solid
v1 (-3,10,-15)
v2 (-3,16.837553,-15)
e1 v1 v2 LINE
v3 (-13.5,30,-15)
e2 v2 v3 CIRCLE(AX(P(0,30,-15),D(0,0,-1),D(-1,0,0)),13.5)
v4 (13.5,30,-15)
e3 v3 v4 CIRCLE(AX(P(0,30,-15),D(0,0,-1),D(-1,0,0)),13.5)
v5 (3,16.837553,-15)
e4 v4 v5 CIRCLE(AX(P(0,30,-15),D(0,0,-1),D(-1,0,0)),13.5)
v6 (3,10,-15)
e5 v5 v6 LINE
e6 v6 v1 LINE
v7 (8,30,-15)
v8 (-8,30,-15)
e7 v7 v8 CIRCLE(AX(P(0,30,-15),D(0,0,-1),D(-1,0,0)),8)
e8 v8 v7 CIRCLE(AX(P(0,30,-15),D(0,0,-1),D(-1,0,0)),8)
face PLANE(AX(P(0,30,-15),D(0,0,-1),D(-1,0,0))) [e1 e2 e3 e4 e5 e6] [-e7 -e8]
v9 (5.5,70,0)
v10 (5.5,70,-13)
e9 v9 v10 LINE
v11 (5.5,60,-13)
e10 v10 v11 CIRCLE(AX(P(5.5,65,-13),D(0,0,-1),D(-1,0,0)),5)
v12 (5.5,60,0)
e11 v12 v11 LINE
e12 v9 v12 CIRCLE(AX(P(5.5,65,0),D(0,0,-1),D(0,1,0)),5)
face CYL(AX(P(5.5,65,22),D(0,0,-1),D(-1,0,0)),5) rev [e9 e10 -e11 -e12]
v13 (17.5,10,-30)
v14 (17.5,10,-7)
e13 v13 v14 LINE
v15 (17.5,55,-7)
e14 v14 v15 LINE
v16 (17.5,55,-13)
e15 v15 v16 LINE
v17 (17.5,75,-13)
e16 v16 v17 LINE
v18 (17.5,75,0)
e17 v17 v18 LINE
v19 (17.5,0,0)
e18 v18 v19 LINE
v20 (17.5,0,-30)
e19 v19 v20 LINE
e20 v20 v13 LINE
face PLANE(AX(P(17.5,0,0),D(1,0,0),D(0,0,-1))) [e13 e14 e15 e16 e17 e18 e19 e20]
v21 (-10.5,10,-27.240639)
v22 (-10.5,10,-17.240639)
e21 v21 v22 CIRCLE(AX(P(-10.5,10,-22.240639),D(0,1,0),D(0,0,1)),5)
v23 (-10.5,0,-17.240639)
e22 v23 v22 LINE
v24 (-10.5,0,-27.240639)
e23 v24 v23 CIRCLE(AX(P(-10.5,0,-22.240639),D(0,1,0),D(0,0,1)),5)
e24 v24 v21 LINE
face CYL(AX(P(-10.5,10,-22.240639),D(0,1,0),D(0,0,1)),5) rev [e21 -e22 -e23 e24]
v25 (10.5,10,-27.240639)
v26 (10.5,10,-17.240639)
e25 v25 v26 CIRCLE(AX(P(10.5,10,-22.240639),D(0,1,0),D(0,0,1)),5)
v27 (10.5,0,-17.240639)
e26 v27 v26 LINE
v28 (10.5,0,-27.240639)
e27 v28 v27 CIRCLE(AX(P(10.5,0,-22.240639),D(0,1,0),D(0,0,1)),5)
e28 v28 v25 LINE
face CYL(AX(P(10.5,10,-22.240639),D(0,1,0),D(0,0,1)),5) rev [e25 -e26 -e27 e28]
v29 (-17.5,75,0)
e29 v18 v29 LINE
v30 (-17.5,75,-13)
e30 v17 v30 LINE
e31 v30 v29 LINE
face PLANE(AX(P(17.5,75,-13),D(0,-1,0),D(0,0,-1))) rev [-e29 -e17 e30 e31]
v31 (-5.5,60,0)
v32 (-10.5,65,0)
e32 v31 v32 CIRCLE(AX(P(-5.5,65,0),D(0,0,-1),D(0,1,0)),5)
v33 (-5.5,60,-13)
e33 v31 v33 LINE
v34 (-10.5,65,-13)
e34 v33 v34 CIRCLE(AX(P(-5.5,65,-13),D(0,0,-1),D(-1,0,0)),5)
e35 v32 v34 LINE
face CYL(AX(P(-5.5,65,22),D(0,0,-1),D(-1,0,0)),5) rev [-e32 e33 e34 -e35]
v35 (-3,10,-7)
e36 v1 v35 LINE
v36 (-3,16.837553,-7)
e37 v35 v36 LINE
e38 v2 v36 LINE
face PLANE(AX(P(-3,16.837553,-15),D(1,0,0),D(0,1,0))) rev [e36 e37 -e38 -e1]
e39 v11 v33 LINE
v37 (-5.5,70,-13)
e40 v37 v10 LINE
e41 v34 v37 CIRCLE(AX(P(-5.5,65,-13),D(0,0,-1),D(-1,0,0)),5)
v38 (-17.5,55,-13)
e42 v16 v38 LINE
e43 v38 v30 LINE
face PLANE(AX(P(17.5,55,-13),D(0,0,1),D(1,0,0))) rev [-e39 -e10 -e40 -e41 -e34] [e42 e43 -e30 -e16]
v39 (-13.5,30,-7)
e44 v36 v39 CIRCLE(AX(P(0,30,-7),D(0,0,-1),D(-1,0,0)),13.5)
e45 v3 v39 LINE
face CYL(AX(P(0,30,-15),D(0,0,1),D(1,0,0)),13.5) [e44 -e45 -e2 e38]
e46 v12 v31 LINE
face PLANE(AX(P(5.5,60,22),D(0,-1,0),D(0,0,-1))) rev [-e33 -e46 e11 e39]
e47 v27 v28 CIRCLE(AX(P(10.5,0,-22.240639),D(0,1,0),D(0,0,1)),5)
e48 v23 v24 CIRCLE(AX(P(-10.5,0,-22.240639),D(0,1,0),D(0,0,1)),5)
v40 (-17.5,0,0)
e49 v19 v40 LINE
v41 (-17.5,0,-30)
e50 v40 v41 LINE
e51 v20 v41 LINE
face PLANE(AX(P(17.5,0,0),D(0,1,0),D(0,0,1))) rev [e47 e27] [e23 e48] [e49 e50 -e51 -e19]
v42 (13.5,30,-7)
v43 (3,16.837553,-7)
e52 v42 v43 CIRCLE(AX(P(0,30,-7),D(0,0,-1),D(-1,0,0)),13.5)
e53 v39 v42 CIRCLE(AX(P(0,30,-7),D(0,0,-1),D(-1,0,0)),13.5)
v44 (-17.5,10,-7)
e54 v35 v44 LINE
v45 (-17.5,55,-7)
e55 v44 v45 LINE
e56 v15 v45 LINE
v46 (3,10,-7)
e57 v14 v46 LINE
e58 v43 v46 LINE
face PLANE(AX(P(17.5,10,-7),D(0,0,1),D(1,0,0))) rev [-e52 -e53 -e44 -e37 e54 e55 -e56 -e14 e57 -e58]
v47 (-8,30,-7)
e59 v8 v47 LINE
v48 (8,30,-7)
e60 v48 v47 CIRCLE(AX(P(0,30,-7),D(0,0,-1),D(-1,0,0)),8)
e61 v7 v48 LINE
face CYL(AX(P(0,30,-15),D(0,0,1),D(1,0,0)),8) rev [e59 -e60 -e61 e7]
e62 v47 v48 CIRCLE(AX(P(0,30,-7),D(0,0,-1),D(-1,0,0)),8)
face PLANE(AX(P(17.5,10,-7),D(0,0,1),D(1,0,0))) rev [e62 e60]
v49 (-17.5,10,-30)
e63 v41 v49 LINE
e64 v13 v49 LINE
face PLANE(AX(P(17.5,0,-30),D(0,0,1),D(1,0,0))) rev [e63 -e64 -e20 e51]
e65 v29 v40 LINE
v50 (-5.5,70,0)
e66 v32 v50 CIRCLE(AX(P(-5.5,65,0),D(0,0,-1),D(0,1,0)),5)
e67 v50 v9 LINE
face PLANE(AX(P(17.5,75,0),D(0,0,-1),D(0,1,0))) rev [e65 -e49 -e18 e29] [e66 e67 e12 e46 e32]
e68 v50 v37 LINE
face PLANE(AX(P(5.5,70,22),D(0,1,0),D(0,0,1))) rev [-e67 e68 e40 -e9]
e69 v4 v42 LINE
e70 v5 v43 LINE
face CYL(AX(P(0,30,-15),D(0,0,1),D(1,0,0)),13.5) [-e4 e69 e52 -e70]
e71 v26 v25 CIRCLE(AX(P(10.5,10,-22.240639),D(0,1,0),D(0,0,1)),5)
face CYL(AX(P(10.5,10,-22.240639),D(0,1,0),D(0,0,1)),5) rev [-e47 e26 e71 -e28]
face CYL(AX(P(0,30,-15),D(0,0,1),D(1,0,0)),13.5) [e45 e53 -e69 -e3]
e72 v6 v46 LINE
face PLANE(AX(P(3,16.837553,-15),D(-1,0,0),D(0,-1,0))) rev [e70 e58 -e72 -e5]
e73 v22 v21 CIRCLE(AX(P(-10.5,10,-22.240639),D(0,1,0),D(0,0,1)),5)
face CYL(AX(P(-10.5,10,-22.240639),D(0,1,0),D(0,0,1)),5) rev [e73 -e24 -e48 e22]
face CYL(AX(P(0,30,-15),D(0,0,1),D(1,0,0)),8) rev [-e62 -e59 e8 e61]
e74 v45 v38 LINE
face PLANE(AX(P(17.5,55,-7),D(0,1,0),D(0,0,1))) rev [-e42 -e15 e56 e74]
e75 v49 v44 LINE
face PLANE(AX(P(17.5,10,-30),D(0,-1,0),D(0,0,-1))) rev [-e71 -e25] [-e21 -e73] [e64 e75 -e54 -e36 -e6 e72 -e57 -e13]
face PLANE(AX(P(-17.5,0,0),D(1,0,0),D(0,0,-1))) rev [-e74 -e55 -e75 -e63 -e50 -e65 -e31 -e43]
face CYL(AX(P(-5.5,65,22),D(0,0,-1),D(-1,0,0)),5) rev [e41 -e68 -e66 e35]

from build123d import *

# Parameters (mm, degrees)
L_BRACKET_BODY_DEPTH         = 17.5
UPRIGHT_SLOT_DEPTH           = 35
CORNER_SUPPORT_BOSS_SKETCH_R = 8
CORNER_SUPPORT_BOSS_DEPTH    = 8
DOWEL_HOLE_10_D              = 10


with BuildPart() as part:
    # L-Bracket Profile Sketch → L-Bracket Body (new, symmetric)
    with BuildSketch(Plane(origin=(0, 0, 0), x_dir=(0, 0, -1), z_dir=(1, 0, 0))):
        Polygon((0, 0), (30, 0), (30, 10), (7, 10), (7, 55), (13, 55), (13, 75), (0, 75), align=None)
    extrude(amount=L_BRACKET_BODY_DEPTH, both=True)

    # Upright Slot Sketch → Upright Slot (cut)
    with BuildSketch(Plane(origin=(0, 0, -13), x_dir=(-1, 0, 0), z_dir=(0, 0, -1))):
        with BuildLine():
            Line((-5.5, 70), (5.5, 70))
            ThreePointArc((5.5, 70), (10.5, 65), (5.5, 60))
            Line((5.5, 60), (-5.5, 60))
            ThreePointArc((-5.5, 60), (-10.5, 65), (-5.5, 70))
        make_face()
    extrude(amount=-UPRIGHT_SLOT_DEPTH, mode=Mode.SUBTRACT)

    # Corner Support Boss Sketch → Corner Support Boss (add)
    with BuildSketch(Plane(origin=(0, 0, -7), x_dir=(-1, 0, 0), z_dir=(0, 0, -1))):
        with BuildLine():
            Line((-3, 16.837553419), (-3, 10))
            Line((-3, 10), (3, 10))
            Line((3, 10), (3, 16.837553419))
            ThreePointArc((3, 16.837553419), (0, 43.5), (-3, 16.837553419))
        make_face()
        with Locations((0, 30)):
            Circle(CORNER_SUPPORT_BOSS_SKETCH_R, mode=Mode.SUBTRACT)
    extrude(amount=CORNER_SUPPORT_BOSS_DEPTH)

    # Dowel Hole Ø10 (through all)
    with Locations(Plane(origin=(0, 10, 0), x_dir=(1, 0, 0), z_dir=(0, 1, 0))):
        with Locations((-10.5, 22.240638775), (10.5, 22.240638775)):
            Hole(DOWEL_HOLE_10_D / 2)


solid = part.part
